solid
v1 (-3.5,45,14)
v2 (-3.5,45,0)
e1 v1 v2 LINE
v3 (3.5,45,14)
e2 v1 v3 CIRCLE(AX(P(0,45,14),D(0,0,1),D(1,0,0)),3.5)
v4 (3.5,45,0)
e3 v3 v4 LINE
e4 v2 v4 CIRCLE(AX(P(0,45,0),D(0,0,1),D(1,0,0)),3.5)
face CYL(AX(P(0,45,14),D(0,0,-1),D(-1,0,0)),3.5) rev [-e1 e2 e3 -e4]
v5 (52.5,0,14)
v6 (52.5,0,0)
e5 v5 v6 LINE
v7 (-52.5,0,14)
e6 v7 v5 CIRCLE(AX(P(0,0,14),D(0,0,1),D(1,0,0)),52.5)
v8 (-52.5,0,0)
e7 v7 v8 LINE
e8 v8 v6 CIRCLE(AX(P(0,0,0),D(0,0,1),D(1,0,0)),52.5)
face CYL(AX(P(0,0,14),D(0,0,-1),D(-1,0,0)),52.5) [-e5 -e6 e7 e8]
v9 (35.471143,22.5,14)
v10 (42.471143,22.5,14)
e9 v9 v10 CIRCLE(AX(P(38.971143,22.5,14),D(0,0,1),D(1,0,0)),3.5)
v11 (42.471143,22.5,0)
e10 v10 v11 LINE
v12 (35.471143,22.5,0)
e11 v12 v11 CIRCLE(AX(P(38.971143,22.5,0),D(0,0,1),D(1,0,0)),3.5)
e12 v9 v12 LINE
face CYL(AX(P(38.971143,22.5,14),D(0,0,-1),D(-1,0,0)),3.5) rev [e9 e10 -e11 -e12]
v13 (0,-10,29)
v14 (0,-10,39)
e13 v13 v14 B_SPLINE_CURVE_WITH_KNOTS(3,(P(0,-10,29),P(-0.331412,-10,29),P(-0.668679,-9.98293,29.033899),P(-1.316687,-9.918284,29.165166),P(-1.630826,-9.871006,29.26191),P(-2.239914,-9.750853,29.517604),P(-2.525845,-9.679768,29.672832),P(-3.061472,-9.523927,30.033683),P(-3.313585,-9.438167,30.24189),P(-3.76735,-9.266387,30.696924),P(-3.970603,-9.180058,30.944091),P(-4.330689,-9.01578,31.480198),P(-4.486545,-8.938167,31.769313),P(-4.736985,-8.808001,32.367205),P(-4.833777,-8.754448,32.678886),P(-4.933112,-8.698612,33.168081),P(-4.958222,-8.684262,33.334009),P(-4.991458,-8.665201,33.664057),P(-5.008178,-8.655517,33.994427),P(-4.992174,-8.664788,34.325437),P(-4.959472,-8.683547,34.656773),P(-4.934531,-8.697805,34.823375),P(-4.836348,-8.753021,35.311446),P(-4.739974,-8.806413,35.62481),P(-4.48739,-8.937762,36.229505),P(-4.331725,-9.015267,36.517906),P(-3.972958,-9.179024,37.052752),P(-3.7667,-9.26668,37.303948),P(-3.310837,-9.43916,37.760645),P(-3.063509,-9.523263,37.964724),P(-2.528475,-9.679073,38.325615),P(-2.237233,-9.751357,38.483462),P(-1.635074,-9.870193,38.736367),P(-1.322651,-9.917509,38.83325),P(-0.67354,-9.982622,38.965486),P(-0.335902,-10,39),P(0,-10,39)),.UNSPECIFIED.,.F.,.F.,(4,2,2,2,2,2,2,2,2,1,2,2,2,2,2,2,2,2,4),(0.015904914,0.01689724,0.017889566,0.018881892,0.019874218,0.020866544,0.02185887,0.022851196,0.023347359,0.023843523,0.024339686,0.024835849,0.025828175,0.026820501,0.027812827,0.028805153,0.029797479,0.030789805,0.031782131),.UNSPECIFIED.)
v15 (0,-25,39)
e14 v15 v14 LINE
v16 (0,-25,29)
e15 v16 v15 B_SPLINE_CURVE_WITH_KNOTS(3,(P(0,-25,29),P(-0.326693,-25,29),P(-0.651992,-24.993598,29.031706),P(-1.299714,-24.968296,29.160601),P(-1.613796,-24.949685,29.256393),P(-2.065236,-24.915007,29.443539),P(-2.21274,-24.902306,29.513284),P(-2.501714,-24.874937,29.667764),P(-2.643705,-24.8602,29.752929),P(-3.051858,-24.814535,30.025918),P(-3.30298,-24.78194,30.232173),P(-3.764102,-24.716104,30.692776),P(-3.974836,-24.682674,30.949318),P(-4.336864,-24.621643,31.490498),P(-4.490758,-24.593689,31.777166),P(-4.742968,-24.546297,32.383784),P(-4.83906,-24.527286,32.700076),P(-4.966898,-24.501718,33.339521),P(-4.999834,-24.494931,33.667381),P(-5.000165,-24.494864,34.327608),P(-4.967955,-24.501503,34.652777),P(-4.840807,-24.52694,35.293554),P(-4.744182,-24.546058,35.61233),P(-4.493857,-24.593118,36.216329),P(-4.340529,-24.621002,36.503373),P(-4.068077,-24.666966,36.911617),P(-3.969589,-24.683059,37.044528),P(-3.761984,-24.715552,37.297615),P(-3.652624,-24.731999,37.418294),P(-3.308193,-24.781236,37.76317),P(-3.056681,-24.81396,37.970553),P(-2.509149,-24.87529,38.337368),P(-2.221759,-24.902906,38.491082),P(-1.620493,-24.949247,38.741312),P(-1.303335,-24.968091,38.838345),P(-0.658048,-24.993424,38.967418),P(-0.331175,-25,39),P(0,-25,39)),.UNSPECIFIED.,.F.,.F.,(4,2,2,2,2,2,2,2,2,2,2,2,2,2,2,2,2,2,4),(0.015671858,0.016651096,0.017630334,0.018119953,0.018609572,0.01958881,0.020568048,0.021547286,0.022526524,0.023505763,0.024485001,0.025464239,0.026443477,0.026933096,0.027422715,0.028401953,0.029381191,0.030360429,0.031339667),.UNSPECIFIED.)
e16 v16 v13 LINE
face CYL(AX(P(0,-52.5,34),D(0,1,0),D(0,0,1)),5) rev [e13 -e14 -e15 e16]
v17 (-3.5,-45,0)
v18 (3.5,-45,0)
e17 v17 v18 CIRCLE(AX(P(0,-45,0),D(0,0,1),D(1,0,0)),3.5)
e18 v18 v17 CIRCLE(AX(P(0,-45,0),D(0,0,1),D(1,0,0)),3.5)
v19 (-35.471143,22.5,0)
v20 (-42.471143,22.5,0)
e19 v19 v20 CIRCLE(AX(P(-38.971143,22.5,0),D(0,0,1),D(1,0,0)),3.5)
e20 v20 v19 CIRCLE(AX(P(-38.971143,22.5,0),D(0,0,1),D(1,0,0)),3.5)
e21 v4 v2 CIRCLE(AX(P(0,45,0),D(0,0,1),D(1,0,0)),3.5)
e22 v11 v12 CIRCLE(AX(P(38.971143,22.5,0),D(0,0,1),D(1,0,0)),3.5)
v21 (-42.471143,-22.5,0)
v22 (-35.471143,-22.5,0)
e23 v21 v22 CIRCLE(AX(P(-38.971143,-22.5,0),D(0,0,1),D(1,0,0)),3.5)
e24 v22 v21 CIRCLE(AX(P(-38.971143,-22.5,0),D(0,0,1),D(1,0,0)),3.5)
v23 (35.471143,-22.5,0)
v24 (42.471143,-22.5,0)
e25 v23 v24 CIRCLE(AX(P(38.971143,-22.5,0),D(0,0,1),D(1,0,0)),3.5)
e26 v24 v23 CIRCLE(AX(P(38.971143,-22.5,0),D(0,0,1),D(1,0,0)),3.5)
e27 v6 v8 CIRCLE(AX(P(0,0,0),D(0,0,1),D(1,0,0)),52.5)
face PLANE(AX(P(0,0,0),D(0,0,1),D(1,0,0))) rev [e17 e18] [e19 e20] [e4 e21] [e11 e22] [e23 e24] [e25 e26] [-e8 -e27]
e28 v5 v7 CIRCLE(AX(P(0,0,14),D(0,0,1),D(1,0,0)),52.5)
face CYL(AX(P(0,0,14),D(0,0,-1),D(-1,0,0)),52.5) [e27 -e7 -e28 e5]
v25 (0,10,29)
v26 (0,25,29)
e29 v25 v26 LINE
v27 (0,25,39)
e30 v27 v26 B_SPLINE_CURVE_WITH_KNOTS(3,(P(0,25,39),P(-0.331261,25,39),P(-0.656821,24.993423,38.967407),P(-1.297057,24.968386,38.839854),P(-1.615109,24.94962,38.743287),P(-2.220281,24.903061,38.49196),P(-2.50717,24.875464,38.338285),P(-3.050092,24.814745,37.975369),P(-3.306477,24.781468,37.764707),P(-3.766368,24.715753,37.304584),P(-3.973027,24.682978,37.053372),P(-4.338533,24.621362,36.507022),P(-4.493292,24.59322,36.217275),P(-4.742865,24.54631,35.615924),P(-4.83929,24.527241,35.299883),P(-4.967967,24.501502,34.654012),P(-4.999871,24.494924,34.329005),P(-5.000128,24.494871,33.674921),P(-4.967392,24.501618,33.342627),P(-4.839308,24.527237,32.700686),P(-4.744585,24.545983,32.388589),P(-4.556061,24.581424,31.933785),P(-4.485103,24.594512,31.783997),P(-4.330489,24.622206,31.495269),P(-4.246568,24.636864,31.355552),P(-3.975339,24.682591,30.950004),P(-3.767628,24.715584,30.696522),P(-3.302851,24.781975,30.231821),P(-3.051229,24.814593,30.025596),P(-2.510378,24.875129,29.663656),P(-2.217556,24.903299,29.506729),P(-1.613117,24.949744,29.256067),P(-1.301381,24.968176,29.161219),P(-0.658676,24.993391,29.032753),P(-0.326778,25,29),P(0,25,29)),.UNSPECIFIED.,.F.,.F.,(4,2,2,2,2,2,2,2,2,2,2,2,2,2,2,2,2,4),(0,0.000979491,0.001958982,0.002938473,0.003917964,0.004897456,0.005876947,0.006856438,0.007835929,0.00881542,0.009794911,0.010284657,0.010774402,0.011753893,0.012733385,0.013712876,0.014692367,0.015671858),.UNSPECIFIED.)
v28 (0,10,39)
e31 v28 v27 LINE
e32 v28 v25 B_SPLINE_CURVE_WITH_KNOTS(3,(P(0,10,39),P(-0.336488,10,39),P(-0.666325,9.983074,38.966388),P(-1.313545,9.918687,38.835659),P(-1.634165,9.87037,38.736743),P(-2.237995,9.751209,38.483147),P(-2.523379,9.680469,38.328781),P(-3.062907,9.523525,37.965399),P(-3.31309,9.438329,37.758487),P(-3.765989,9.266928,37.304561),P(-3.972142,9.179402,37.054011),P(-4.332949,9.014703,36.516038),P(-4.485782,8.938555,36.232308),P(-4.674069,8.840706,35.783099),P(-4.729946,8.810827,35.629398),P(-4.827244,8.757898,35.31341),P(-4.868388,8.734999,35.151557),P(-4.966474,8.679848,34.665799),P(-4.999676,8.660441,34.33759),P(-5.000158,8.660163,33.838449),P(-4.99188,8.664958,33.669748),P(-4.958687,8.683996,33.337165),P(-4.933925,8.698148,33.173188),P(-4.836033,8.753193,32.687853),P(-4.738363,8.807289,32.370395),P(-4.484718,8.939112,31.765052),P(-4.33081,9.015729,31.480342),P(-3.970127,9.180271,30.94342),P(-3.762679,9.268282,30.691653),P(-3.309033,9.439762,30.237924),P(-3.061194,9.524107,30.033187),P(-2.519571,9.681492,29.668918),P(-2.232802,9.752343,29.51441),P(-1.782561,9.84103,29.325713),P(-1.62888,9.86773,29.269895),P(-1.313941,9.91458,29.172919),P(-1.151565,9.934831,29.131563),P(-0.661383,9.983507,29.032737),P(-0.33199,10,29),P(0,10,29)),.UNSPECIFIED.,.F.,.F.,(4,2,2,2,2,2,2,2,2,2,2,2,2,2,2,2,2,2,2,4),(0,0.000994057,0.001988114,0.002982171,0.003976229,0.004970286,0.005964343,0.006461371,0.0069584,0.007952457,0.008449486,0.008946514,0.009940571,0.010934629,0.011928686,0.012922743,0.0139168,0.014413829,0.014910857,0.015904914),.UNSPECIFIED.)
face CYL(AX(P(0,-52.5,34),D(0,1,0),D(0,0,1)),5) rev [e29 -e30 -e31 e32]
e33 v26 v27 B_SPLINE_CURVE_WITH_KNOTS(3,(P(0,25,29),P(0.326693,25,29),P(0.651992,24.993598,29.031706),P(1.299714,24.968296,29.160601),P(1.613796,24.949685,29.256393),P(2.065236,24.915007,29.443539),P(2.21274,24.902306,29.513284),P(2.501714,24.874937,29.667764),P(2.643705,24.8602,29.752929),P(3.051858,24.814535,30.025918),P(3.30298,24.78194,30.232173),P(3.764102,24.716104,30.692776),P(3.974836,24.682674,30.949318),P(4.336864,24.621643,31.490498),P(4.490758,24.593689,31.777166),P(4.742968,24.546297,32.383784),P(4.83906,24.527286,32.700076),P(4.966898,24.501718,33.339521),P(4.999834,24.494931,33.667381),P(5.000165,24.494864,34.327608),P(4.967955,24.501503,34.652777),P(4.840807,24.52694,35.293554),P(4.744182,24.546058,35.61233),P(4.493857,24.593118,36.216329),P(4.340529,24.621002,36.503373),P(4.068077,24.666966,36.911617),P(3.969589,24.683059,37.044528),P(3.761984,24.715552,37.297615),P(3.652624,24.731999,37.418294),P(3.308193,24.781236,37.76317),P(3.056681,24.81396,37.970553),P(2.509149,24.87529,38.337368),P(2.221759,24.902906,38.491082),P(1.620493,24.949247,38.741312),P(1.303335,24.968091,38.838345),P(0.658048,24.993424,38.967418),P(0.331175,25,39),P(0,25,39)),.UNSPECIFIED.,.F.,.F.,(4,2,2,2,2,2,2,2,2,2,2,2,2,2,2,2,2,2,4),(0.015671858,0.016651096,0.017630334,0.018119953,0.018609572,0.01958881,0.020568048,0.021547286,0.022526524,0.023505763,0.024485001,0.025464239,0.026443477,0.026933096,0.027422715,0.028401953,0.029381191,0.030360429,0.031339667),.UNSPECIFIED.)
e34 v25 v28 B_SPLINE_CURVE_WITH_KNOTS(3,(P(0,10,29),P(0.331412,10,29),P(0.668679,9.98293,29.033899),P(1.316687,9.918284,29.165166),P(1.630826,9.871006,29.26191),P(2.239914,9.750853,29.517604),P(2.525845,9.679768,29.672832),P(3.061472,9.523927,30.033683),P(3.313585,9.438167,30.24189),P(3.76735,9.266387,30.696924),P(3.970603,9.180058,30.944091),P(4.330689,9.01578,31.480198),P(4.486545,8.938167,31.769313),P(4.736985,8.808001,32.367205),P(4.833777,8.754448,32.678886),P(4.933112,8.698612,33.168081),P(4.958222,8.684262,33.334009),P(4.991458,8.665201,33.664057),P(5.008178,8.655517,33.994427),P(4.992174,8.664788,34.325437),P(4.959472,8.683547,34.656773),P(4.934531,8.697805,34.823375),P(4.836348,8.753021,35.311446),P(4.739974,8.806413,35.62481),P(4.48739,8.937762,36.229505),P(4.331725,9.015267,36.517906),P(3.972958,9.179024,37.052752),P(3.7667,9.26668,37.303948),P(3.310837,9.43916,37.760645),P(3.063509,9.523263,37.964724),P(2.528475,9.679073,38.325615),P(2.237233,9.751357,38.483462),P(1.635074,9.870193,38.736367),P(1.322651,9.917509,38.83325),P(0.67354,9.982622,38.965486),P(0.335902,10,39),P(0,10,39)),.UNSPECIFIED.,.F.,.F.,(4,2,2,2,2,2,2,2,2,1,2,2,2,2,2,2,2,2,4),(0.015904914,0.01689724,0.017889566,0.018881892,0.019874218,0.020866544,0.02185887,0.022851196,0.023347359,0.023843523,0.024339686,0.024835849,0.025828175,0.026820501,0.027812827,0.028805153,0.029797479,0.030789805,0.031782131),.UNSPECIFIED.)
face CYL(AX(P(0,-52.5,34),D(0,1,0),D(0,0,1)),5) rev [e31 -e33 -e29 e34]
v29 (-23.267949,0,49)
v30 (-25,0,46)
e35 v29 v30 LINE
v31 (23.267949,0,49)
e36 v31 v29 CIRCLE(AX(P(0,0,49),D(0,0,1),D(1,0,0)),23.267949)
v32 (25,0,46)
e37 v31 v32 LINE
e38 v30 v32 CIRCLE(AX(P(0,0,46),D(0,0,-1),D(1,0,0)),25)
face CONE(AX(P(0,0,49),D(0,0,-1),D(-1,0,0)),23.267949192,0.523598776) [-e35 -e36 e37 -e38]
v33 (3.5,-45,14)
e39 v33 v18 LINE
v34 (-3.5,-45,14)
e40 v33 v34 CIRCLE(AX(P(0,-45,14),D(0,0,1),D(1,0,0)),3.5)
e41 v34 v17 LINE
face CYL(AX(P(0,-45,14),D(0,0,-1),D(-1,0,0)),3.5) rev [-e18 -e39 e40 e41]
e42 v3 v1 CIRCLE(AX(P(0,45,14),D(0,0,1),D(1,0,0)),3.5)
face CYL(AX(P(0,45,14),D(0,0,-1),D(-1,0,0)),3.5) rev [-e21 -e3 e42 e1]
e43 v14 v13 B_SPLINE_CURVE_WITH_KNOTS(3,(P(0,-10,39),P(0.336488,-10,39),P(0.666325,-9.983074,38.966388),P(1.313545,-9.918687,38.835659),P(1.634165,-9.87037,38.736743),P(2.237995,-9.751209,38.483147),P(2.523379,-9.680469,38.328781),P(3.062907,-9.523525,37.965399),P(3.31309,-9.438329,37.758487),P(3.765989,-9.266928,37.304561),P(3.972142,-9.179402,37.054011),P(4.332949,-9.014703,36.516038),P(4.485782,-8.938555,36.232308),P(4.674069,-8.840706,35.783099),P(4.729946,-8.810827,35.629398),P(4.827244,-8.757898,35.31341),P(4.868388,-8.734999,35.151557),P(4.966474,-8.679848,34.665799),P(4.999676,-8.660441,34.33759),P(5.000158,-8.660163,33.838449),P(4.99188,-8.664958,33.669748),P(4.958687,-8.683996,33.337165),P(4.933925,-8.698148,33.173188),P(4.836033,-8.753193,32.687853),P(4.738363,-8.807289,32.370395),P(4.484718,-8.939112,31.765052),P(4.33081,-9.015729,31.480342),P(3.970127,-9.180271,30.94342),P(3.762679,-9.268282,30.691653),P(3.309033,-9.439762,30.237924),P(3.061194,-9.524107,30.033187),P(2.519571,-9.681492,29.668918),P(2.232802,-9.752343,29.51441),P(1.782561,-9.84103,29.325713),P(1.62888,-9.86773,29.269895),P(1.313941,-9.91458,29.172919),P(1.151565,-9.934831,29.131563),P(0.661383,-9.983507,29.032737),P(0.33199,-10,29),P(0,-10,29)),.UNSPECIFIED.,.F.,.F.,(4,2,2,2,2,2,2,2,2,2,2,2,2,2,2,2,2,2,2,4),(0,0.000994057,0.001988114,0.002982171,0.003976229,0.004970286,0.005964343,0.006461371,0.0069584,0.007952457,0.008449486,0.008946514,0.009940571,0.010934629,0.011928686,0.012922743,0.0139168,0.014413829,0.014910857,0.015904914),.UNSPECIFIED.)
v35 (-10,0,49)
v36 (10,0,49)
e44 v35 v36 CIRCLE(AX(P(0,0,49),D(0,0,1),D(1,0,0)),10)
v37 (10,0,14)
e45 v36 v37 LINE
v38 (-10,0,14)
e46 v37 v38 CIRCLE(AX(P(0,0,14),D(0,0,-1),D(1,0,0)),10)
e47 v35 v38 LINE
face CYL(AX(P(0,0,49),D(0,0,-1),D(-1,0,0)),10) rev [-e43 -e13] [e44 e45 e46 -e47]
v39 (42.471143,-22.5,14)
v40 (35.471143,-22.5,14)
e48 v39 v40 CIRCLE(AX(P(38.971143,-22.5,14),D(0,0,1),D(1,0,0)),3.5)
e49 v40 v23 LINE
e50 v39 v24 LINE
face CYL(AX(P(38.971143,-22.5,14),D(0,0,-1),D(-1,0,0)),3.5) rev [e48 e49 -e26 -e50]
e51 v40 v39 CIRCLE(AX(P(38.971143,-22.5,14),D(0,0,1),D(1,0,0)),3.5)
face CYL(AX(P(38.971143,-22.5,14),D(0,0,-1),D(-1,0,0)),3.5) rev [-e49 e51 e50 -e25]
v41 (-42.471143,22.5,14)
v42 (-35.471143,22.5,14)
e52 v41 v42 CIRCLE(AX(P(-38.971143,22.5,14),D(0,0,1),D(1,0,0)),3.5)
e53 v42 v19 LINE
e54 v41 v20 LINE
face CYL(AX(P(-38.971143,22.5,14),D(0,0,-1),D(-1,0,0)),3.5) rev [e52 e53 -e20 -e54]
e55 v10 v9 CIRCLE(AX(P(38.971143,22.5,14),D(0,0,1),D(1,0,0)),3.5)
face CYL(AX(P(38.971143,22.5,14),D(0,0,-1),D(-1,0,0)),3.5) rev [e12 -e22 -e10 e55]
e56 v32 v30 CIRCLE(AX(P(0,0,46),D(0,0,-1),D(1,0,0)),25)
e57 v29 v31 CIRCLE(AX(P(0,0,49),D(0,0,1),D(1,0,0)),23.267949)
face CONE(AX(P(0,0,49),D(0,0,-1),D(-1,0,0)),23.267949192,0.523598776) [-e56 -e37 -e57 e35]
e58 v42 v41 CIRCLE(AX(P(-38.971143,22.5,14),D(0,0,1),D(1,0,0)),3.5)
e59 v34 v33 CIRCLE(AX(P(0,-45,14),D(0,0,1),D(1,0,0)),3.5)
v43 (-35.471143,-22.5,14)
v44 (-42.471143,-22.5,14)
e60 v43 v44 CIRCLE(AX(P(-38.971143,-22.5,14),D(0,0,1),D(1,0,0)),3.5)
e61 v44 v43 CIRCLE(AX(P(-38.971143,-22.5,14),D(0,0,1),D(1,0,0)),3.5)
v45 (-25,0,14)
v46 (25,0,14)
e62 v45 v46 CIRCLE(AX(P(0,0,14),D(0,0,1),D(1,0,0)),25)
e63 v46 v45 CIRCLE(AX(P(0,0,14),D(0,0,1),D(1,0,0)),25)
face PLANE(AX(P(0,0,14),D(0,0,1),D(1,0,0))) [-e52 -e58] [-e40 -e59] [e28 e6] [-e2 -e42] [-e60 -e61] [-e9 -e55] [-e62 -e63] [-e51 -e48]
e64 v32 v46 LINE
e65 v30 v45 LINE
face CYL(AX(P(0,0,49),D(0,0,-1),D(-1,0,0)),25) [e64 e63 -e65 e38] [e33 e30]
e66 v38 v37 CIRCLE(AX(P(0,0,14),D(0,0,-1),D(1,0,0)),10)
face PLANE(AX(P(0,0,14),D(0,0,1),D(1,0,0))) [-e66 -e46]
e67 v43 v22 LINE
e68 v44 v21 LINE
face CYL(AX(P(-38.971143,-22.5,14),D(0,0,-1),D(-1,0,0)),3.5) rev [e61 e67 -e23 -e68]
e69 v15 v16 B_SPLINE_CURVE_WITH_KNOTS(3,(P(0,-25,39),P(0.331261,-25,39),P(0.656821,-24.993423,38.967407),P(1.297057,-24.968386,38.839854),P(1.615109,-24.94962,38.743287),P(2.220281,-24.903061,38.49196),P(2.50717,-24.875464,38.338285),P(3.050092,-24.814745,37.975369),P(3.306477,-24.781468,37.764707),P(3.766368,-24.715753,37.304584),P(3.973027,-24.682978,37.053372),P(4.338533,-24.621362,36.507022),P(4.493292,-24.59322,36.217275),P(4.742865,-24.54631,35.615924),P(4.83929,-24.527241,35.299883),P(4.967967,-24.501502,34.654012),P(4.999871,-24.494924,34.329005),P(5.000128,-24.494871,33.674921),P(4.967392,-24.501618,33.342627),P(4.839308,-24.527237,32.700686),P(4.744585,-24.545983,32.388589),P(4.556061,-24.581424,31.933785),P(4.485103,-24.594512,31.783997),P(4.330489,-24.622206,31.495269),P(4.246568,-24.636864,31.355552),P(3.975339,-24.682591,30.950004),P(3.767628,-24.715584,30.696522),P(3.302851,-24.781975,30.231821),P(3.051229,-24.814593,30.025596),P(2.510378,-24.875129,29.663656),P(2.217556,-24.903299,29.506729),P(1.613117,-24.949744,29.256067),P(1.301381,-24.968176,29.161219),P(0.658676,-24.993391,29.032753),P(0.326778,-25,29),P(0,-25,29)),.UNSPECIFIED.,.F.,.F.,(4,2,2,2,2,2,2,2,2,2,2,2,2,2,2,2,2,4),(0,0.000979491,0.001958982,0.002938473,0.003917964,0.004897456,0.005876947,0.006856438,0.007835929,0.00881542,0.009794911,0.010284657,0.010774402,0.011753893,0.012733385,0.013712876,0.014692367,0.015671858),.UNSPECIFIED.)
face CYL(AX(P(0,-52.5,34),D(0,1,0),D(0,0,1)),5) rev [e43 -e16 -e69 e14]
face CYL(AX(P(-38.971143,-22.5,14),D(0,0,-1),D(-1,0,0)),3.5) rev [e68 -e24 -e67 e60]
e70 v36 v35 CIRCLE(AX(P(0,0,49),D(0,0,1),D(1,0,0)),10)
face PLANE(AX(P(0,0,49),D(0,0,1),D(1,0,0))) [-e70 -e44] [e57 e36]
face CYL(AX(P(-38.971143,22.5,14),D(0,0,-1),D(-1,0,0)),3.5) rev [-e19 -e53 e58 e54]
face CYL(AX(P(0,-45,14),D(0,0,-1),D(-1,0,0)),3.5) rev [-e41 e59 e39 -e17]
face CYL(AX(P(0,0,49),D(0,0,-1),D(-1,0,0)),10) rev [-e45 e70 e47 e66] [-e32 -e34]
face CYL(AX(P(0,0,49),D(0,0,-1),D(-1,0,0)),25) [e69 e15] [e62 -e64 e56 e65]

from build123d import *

# Parameters (mm, degrees)
SKETCH1_R               = 52.5
SKETCH1_R_2             = 3.5
BOSS_EXTRUDE1_DEPTH     = 14
SKETCH2_R               = 25
SKETCH2_R_2             = 10
BOSS_EXTRUDE2_DEPTH     = 35
CUT_EXTRUDE1_DEPTH      = 89.95785519
CUT_EXTRUDE1_DEPTH_BACK = 89.95785519
SKETCH3_R               = 5
CHAMFER1_SIZE           = 3
CHAMFER1_SIZE2          = 1.732050808


with BuildPart() as part:
    # Sketch1 → Boss-Extrude1 (new body)
    with BuildSketch(Plane.XY):
        Circle(SKETCH1_R)
        with Locations((0, 45)):
            Circle(SKETCH1_R_2, mode=Mode.SUBTRACT)
        with Locations((38.97114317, 22.5)):
            Circle(SKETCH1_R_2, mode=Mode.SUBTRACT)
        with Locations((38.97114317, -22.5)):
            Circle(SKETCH1_R_2, mode=Mode.SUBTRACT)
        with Locations((0, -45)):
            Circle(SKETCH1_R_2, mode=Mode.SUBTRACT)
        with Locations((-38.97114317, -22.5)):
            Circle(SKETCH1_R_2, mode=Mode.SUBTRACT)
        with Locations((-38.97114317, 22.5)):
            Circle(SKETCH1_R_2, mode=Mode.SUBTRACT)
    extrude(amount=BOSS_EXTRUDE1_DEPTH)

    # Sketch2 → Boss-Extrude2 (add)
    with BuildSketch(Plane.XY.offset(14)):
        Circle(SKETCH2_R)
        Circle(SKETCH2_R_2, mode=Mode.SUBTRACT)
    extrude(amount=BOSS_EXTRUDE2_DEPTH)

    # Sketch3 → Cut-Extrude1 (cut, two sides: drawn at the far end of the back side and taken through both)
    with BuildSketch(Plane(origin=(0, 0, 0), x_dir=(1, 0, 0), z_dir=(0, 1, 0)).offset(-CUT_EXTRUDE1_DEPTH_BACK)):
        with Locations(Location((0, -34, 0), (0, 0, 270))):
            Circle(SKETCH3_R)
    extrude(amount=CUT_EXTRUDE1_DEPTH + CUT_EXTRUDE1_DEPTH_BACK, mode=Mode.SUBTRACT)

    # Chamfer1
    chamfer1_edges = [part.edges().sort_by_distance(p)[0] for p in [
        (-25, 0, 49),
    ]]
    chamfer1_side = [part.faces().sort_by_distance(p)[0] for p in [
        (-25, 0, 31.5),
    ]]
    chamfer(chamfer1_edges, length=CHAMFER1_SIZE, length2=CHAMFER1_SIZE2, reference=chamfer1_side[0])


solid = part.part
